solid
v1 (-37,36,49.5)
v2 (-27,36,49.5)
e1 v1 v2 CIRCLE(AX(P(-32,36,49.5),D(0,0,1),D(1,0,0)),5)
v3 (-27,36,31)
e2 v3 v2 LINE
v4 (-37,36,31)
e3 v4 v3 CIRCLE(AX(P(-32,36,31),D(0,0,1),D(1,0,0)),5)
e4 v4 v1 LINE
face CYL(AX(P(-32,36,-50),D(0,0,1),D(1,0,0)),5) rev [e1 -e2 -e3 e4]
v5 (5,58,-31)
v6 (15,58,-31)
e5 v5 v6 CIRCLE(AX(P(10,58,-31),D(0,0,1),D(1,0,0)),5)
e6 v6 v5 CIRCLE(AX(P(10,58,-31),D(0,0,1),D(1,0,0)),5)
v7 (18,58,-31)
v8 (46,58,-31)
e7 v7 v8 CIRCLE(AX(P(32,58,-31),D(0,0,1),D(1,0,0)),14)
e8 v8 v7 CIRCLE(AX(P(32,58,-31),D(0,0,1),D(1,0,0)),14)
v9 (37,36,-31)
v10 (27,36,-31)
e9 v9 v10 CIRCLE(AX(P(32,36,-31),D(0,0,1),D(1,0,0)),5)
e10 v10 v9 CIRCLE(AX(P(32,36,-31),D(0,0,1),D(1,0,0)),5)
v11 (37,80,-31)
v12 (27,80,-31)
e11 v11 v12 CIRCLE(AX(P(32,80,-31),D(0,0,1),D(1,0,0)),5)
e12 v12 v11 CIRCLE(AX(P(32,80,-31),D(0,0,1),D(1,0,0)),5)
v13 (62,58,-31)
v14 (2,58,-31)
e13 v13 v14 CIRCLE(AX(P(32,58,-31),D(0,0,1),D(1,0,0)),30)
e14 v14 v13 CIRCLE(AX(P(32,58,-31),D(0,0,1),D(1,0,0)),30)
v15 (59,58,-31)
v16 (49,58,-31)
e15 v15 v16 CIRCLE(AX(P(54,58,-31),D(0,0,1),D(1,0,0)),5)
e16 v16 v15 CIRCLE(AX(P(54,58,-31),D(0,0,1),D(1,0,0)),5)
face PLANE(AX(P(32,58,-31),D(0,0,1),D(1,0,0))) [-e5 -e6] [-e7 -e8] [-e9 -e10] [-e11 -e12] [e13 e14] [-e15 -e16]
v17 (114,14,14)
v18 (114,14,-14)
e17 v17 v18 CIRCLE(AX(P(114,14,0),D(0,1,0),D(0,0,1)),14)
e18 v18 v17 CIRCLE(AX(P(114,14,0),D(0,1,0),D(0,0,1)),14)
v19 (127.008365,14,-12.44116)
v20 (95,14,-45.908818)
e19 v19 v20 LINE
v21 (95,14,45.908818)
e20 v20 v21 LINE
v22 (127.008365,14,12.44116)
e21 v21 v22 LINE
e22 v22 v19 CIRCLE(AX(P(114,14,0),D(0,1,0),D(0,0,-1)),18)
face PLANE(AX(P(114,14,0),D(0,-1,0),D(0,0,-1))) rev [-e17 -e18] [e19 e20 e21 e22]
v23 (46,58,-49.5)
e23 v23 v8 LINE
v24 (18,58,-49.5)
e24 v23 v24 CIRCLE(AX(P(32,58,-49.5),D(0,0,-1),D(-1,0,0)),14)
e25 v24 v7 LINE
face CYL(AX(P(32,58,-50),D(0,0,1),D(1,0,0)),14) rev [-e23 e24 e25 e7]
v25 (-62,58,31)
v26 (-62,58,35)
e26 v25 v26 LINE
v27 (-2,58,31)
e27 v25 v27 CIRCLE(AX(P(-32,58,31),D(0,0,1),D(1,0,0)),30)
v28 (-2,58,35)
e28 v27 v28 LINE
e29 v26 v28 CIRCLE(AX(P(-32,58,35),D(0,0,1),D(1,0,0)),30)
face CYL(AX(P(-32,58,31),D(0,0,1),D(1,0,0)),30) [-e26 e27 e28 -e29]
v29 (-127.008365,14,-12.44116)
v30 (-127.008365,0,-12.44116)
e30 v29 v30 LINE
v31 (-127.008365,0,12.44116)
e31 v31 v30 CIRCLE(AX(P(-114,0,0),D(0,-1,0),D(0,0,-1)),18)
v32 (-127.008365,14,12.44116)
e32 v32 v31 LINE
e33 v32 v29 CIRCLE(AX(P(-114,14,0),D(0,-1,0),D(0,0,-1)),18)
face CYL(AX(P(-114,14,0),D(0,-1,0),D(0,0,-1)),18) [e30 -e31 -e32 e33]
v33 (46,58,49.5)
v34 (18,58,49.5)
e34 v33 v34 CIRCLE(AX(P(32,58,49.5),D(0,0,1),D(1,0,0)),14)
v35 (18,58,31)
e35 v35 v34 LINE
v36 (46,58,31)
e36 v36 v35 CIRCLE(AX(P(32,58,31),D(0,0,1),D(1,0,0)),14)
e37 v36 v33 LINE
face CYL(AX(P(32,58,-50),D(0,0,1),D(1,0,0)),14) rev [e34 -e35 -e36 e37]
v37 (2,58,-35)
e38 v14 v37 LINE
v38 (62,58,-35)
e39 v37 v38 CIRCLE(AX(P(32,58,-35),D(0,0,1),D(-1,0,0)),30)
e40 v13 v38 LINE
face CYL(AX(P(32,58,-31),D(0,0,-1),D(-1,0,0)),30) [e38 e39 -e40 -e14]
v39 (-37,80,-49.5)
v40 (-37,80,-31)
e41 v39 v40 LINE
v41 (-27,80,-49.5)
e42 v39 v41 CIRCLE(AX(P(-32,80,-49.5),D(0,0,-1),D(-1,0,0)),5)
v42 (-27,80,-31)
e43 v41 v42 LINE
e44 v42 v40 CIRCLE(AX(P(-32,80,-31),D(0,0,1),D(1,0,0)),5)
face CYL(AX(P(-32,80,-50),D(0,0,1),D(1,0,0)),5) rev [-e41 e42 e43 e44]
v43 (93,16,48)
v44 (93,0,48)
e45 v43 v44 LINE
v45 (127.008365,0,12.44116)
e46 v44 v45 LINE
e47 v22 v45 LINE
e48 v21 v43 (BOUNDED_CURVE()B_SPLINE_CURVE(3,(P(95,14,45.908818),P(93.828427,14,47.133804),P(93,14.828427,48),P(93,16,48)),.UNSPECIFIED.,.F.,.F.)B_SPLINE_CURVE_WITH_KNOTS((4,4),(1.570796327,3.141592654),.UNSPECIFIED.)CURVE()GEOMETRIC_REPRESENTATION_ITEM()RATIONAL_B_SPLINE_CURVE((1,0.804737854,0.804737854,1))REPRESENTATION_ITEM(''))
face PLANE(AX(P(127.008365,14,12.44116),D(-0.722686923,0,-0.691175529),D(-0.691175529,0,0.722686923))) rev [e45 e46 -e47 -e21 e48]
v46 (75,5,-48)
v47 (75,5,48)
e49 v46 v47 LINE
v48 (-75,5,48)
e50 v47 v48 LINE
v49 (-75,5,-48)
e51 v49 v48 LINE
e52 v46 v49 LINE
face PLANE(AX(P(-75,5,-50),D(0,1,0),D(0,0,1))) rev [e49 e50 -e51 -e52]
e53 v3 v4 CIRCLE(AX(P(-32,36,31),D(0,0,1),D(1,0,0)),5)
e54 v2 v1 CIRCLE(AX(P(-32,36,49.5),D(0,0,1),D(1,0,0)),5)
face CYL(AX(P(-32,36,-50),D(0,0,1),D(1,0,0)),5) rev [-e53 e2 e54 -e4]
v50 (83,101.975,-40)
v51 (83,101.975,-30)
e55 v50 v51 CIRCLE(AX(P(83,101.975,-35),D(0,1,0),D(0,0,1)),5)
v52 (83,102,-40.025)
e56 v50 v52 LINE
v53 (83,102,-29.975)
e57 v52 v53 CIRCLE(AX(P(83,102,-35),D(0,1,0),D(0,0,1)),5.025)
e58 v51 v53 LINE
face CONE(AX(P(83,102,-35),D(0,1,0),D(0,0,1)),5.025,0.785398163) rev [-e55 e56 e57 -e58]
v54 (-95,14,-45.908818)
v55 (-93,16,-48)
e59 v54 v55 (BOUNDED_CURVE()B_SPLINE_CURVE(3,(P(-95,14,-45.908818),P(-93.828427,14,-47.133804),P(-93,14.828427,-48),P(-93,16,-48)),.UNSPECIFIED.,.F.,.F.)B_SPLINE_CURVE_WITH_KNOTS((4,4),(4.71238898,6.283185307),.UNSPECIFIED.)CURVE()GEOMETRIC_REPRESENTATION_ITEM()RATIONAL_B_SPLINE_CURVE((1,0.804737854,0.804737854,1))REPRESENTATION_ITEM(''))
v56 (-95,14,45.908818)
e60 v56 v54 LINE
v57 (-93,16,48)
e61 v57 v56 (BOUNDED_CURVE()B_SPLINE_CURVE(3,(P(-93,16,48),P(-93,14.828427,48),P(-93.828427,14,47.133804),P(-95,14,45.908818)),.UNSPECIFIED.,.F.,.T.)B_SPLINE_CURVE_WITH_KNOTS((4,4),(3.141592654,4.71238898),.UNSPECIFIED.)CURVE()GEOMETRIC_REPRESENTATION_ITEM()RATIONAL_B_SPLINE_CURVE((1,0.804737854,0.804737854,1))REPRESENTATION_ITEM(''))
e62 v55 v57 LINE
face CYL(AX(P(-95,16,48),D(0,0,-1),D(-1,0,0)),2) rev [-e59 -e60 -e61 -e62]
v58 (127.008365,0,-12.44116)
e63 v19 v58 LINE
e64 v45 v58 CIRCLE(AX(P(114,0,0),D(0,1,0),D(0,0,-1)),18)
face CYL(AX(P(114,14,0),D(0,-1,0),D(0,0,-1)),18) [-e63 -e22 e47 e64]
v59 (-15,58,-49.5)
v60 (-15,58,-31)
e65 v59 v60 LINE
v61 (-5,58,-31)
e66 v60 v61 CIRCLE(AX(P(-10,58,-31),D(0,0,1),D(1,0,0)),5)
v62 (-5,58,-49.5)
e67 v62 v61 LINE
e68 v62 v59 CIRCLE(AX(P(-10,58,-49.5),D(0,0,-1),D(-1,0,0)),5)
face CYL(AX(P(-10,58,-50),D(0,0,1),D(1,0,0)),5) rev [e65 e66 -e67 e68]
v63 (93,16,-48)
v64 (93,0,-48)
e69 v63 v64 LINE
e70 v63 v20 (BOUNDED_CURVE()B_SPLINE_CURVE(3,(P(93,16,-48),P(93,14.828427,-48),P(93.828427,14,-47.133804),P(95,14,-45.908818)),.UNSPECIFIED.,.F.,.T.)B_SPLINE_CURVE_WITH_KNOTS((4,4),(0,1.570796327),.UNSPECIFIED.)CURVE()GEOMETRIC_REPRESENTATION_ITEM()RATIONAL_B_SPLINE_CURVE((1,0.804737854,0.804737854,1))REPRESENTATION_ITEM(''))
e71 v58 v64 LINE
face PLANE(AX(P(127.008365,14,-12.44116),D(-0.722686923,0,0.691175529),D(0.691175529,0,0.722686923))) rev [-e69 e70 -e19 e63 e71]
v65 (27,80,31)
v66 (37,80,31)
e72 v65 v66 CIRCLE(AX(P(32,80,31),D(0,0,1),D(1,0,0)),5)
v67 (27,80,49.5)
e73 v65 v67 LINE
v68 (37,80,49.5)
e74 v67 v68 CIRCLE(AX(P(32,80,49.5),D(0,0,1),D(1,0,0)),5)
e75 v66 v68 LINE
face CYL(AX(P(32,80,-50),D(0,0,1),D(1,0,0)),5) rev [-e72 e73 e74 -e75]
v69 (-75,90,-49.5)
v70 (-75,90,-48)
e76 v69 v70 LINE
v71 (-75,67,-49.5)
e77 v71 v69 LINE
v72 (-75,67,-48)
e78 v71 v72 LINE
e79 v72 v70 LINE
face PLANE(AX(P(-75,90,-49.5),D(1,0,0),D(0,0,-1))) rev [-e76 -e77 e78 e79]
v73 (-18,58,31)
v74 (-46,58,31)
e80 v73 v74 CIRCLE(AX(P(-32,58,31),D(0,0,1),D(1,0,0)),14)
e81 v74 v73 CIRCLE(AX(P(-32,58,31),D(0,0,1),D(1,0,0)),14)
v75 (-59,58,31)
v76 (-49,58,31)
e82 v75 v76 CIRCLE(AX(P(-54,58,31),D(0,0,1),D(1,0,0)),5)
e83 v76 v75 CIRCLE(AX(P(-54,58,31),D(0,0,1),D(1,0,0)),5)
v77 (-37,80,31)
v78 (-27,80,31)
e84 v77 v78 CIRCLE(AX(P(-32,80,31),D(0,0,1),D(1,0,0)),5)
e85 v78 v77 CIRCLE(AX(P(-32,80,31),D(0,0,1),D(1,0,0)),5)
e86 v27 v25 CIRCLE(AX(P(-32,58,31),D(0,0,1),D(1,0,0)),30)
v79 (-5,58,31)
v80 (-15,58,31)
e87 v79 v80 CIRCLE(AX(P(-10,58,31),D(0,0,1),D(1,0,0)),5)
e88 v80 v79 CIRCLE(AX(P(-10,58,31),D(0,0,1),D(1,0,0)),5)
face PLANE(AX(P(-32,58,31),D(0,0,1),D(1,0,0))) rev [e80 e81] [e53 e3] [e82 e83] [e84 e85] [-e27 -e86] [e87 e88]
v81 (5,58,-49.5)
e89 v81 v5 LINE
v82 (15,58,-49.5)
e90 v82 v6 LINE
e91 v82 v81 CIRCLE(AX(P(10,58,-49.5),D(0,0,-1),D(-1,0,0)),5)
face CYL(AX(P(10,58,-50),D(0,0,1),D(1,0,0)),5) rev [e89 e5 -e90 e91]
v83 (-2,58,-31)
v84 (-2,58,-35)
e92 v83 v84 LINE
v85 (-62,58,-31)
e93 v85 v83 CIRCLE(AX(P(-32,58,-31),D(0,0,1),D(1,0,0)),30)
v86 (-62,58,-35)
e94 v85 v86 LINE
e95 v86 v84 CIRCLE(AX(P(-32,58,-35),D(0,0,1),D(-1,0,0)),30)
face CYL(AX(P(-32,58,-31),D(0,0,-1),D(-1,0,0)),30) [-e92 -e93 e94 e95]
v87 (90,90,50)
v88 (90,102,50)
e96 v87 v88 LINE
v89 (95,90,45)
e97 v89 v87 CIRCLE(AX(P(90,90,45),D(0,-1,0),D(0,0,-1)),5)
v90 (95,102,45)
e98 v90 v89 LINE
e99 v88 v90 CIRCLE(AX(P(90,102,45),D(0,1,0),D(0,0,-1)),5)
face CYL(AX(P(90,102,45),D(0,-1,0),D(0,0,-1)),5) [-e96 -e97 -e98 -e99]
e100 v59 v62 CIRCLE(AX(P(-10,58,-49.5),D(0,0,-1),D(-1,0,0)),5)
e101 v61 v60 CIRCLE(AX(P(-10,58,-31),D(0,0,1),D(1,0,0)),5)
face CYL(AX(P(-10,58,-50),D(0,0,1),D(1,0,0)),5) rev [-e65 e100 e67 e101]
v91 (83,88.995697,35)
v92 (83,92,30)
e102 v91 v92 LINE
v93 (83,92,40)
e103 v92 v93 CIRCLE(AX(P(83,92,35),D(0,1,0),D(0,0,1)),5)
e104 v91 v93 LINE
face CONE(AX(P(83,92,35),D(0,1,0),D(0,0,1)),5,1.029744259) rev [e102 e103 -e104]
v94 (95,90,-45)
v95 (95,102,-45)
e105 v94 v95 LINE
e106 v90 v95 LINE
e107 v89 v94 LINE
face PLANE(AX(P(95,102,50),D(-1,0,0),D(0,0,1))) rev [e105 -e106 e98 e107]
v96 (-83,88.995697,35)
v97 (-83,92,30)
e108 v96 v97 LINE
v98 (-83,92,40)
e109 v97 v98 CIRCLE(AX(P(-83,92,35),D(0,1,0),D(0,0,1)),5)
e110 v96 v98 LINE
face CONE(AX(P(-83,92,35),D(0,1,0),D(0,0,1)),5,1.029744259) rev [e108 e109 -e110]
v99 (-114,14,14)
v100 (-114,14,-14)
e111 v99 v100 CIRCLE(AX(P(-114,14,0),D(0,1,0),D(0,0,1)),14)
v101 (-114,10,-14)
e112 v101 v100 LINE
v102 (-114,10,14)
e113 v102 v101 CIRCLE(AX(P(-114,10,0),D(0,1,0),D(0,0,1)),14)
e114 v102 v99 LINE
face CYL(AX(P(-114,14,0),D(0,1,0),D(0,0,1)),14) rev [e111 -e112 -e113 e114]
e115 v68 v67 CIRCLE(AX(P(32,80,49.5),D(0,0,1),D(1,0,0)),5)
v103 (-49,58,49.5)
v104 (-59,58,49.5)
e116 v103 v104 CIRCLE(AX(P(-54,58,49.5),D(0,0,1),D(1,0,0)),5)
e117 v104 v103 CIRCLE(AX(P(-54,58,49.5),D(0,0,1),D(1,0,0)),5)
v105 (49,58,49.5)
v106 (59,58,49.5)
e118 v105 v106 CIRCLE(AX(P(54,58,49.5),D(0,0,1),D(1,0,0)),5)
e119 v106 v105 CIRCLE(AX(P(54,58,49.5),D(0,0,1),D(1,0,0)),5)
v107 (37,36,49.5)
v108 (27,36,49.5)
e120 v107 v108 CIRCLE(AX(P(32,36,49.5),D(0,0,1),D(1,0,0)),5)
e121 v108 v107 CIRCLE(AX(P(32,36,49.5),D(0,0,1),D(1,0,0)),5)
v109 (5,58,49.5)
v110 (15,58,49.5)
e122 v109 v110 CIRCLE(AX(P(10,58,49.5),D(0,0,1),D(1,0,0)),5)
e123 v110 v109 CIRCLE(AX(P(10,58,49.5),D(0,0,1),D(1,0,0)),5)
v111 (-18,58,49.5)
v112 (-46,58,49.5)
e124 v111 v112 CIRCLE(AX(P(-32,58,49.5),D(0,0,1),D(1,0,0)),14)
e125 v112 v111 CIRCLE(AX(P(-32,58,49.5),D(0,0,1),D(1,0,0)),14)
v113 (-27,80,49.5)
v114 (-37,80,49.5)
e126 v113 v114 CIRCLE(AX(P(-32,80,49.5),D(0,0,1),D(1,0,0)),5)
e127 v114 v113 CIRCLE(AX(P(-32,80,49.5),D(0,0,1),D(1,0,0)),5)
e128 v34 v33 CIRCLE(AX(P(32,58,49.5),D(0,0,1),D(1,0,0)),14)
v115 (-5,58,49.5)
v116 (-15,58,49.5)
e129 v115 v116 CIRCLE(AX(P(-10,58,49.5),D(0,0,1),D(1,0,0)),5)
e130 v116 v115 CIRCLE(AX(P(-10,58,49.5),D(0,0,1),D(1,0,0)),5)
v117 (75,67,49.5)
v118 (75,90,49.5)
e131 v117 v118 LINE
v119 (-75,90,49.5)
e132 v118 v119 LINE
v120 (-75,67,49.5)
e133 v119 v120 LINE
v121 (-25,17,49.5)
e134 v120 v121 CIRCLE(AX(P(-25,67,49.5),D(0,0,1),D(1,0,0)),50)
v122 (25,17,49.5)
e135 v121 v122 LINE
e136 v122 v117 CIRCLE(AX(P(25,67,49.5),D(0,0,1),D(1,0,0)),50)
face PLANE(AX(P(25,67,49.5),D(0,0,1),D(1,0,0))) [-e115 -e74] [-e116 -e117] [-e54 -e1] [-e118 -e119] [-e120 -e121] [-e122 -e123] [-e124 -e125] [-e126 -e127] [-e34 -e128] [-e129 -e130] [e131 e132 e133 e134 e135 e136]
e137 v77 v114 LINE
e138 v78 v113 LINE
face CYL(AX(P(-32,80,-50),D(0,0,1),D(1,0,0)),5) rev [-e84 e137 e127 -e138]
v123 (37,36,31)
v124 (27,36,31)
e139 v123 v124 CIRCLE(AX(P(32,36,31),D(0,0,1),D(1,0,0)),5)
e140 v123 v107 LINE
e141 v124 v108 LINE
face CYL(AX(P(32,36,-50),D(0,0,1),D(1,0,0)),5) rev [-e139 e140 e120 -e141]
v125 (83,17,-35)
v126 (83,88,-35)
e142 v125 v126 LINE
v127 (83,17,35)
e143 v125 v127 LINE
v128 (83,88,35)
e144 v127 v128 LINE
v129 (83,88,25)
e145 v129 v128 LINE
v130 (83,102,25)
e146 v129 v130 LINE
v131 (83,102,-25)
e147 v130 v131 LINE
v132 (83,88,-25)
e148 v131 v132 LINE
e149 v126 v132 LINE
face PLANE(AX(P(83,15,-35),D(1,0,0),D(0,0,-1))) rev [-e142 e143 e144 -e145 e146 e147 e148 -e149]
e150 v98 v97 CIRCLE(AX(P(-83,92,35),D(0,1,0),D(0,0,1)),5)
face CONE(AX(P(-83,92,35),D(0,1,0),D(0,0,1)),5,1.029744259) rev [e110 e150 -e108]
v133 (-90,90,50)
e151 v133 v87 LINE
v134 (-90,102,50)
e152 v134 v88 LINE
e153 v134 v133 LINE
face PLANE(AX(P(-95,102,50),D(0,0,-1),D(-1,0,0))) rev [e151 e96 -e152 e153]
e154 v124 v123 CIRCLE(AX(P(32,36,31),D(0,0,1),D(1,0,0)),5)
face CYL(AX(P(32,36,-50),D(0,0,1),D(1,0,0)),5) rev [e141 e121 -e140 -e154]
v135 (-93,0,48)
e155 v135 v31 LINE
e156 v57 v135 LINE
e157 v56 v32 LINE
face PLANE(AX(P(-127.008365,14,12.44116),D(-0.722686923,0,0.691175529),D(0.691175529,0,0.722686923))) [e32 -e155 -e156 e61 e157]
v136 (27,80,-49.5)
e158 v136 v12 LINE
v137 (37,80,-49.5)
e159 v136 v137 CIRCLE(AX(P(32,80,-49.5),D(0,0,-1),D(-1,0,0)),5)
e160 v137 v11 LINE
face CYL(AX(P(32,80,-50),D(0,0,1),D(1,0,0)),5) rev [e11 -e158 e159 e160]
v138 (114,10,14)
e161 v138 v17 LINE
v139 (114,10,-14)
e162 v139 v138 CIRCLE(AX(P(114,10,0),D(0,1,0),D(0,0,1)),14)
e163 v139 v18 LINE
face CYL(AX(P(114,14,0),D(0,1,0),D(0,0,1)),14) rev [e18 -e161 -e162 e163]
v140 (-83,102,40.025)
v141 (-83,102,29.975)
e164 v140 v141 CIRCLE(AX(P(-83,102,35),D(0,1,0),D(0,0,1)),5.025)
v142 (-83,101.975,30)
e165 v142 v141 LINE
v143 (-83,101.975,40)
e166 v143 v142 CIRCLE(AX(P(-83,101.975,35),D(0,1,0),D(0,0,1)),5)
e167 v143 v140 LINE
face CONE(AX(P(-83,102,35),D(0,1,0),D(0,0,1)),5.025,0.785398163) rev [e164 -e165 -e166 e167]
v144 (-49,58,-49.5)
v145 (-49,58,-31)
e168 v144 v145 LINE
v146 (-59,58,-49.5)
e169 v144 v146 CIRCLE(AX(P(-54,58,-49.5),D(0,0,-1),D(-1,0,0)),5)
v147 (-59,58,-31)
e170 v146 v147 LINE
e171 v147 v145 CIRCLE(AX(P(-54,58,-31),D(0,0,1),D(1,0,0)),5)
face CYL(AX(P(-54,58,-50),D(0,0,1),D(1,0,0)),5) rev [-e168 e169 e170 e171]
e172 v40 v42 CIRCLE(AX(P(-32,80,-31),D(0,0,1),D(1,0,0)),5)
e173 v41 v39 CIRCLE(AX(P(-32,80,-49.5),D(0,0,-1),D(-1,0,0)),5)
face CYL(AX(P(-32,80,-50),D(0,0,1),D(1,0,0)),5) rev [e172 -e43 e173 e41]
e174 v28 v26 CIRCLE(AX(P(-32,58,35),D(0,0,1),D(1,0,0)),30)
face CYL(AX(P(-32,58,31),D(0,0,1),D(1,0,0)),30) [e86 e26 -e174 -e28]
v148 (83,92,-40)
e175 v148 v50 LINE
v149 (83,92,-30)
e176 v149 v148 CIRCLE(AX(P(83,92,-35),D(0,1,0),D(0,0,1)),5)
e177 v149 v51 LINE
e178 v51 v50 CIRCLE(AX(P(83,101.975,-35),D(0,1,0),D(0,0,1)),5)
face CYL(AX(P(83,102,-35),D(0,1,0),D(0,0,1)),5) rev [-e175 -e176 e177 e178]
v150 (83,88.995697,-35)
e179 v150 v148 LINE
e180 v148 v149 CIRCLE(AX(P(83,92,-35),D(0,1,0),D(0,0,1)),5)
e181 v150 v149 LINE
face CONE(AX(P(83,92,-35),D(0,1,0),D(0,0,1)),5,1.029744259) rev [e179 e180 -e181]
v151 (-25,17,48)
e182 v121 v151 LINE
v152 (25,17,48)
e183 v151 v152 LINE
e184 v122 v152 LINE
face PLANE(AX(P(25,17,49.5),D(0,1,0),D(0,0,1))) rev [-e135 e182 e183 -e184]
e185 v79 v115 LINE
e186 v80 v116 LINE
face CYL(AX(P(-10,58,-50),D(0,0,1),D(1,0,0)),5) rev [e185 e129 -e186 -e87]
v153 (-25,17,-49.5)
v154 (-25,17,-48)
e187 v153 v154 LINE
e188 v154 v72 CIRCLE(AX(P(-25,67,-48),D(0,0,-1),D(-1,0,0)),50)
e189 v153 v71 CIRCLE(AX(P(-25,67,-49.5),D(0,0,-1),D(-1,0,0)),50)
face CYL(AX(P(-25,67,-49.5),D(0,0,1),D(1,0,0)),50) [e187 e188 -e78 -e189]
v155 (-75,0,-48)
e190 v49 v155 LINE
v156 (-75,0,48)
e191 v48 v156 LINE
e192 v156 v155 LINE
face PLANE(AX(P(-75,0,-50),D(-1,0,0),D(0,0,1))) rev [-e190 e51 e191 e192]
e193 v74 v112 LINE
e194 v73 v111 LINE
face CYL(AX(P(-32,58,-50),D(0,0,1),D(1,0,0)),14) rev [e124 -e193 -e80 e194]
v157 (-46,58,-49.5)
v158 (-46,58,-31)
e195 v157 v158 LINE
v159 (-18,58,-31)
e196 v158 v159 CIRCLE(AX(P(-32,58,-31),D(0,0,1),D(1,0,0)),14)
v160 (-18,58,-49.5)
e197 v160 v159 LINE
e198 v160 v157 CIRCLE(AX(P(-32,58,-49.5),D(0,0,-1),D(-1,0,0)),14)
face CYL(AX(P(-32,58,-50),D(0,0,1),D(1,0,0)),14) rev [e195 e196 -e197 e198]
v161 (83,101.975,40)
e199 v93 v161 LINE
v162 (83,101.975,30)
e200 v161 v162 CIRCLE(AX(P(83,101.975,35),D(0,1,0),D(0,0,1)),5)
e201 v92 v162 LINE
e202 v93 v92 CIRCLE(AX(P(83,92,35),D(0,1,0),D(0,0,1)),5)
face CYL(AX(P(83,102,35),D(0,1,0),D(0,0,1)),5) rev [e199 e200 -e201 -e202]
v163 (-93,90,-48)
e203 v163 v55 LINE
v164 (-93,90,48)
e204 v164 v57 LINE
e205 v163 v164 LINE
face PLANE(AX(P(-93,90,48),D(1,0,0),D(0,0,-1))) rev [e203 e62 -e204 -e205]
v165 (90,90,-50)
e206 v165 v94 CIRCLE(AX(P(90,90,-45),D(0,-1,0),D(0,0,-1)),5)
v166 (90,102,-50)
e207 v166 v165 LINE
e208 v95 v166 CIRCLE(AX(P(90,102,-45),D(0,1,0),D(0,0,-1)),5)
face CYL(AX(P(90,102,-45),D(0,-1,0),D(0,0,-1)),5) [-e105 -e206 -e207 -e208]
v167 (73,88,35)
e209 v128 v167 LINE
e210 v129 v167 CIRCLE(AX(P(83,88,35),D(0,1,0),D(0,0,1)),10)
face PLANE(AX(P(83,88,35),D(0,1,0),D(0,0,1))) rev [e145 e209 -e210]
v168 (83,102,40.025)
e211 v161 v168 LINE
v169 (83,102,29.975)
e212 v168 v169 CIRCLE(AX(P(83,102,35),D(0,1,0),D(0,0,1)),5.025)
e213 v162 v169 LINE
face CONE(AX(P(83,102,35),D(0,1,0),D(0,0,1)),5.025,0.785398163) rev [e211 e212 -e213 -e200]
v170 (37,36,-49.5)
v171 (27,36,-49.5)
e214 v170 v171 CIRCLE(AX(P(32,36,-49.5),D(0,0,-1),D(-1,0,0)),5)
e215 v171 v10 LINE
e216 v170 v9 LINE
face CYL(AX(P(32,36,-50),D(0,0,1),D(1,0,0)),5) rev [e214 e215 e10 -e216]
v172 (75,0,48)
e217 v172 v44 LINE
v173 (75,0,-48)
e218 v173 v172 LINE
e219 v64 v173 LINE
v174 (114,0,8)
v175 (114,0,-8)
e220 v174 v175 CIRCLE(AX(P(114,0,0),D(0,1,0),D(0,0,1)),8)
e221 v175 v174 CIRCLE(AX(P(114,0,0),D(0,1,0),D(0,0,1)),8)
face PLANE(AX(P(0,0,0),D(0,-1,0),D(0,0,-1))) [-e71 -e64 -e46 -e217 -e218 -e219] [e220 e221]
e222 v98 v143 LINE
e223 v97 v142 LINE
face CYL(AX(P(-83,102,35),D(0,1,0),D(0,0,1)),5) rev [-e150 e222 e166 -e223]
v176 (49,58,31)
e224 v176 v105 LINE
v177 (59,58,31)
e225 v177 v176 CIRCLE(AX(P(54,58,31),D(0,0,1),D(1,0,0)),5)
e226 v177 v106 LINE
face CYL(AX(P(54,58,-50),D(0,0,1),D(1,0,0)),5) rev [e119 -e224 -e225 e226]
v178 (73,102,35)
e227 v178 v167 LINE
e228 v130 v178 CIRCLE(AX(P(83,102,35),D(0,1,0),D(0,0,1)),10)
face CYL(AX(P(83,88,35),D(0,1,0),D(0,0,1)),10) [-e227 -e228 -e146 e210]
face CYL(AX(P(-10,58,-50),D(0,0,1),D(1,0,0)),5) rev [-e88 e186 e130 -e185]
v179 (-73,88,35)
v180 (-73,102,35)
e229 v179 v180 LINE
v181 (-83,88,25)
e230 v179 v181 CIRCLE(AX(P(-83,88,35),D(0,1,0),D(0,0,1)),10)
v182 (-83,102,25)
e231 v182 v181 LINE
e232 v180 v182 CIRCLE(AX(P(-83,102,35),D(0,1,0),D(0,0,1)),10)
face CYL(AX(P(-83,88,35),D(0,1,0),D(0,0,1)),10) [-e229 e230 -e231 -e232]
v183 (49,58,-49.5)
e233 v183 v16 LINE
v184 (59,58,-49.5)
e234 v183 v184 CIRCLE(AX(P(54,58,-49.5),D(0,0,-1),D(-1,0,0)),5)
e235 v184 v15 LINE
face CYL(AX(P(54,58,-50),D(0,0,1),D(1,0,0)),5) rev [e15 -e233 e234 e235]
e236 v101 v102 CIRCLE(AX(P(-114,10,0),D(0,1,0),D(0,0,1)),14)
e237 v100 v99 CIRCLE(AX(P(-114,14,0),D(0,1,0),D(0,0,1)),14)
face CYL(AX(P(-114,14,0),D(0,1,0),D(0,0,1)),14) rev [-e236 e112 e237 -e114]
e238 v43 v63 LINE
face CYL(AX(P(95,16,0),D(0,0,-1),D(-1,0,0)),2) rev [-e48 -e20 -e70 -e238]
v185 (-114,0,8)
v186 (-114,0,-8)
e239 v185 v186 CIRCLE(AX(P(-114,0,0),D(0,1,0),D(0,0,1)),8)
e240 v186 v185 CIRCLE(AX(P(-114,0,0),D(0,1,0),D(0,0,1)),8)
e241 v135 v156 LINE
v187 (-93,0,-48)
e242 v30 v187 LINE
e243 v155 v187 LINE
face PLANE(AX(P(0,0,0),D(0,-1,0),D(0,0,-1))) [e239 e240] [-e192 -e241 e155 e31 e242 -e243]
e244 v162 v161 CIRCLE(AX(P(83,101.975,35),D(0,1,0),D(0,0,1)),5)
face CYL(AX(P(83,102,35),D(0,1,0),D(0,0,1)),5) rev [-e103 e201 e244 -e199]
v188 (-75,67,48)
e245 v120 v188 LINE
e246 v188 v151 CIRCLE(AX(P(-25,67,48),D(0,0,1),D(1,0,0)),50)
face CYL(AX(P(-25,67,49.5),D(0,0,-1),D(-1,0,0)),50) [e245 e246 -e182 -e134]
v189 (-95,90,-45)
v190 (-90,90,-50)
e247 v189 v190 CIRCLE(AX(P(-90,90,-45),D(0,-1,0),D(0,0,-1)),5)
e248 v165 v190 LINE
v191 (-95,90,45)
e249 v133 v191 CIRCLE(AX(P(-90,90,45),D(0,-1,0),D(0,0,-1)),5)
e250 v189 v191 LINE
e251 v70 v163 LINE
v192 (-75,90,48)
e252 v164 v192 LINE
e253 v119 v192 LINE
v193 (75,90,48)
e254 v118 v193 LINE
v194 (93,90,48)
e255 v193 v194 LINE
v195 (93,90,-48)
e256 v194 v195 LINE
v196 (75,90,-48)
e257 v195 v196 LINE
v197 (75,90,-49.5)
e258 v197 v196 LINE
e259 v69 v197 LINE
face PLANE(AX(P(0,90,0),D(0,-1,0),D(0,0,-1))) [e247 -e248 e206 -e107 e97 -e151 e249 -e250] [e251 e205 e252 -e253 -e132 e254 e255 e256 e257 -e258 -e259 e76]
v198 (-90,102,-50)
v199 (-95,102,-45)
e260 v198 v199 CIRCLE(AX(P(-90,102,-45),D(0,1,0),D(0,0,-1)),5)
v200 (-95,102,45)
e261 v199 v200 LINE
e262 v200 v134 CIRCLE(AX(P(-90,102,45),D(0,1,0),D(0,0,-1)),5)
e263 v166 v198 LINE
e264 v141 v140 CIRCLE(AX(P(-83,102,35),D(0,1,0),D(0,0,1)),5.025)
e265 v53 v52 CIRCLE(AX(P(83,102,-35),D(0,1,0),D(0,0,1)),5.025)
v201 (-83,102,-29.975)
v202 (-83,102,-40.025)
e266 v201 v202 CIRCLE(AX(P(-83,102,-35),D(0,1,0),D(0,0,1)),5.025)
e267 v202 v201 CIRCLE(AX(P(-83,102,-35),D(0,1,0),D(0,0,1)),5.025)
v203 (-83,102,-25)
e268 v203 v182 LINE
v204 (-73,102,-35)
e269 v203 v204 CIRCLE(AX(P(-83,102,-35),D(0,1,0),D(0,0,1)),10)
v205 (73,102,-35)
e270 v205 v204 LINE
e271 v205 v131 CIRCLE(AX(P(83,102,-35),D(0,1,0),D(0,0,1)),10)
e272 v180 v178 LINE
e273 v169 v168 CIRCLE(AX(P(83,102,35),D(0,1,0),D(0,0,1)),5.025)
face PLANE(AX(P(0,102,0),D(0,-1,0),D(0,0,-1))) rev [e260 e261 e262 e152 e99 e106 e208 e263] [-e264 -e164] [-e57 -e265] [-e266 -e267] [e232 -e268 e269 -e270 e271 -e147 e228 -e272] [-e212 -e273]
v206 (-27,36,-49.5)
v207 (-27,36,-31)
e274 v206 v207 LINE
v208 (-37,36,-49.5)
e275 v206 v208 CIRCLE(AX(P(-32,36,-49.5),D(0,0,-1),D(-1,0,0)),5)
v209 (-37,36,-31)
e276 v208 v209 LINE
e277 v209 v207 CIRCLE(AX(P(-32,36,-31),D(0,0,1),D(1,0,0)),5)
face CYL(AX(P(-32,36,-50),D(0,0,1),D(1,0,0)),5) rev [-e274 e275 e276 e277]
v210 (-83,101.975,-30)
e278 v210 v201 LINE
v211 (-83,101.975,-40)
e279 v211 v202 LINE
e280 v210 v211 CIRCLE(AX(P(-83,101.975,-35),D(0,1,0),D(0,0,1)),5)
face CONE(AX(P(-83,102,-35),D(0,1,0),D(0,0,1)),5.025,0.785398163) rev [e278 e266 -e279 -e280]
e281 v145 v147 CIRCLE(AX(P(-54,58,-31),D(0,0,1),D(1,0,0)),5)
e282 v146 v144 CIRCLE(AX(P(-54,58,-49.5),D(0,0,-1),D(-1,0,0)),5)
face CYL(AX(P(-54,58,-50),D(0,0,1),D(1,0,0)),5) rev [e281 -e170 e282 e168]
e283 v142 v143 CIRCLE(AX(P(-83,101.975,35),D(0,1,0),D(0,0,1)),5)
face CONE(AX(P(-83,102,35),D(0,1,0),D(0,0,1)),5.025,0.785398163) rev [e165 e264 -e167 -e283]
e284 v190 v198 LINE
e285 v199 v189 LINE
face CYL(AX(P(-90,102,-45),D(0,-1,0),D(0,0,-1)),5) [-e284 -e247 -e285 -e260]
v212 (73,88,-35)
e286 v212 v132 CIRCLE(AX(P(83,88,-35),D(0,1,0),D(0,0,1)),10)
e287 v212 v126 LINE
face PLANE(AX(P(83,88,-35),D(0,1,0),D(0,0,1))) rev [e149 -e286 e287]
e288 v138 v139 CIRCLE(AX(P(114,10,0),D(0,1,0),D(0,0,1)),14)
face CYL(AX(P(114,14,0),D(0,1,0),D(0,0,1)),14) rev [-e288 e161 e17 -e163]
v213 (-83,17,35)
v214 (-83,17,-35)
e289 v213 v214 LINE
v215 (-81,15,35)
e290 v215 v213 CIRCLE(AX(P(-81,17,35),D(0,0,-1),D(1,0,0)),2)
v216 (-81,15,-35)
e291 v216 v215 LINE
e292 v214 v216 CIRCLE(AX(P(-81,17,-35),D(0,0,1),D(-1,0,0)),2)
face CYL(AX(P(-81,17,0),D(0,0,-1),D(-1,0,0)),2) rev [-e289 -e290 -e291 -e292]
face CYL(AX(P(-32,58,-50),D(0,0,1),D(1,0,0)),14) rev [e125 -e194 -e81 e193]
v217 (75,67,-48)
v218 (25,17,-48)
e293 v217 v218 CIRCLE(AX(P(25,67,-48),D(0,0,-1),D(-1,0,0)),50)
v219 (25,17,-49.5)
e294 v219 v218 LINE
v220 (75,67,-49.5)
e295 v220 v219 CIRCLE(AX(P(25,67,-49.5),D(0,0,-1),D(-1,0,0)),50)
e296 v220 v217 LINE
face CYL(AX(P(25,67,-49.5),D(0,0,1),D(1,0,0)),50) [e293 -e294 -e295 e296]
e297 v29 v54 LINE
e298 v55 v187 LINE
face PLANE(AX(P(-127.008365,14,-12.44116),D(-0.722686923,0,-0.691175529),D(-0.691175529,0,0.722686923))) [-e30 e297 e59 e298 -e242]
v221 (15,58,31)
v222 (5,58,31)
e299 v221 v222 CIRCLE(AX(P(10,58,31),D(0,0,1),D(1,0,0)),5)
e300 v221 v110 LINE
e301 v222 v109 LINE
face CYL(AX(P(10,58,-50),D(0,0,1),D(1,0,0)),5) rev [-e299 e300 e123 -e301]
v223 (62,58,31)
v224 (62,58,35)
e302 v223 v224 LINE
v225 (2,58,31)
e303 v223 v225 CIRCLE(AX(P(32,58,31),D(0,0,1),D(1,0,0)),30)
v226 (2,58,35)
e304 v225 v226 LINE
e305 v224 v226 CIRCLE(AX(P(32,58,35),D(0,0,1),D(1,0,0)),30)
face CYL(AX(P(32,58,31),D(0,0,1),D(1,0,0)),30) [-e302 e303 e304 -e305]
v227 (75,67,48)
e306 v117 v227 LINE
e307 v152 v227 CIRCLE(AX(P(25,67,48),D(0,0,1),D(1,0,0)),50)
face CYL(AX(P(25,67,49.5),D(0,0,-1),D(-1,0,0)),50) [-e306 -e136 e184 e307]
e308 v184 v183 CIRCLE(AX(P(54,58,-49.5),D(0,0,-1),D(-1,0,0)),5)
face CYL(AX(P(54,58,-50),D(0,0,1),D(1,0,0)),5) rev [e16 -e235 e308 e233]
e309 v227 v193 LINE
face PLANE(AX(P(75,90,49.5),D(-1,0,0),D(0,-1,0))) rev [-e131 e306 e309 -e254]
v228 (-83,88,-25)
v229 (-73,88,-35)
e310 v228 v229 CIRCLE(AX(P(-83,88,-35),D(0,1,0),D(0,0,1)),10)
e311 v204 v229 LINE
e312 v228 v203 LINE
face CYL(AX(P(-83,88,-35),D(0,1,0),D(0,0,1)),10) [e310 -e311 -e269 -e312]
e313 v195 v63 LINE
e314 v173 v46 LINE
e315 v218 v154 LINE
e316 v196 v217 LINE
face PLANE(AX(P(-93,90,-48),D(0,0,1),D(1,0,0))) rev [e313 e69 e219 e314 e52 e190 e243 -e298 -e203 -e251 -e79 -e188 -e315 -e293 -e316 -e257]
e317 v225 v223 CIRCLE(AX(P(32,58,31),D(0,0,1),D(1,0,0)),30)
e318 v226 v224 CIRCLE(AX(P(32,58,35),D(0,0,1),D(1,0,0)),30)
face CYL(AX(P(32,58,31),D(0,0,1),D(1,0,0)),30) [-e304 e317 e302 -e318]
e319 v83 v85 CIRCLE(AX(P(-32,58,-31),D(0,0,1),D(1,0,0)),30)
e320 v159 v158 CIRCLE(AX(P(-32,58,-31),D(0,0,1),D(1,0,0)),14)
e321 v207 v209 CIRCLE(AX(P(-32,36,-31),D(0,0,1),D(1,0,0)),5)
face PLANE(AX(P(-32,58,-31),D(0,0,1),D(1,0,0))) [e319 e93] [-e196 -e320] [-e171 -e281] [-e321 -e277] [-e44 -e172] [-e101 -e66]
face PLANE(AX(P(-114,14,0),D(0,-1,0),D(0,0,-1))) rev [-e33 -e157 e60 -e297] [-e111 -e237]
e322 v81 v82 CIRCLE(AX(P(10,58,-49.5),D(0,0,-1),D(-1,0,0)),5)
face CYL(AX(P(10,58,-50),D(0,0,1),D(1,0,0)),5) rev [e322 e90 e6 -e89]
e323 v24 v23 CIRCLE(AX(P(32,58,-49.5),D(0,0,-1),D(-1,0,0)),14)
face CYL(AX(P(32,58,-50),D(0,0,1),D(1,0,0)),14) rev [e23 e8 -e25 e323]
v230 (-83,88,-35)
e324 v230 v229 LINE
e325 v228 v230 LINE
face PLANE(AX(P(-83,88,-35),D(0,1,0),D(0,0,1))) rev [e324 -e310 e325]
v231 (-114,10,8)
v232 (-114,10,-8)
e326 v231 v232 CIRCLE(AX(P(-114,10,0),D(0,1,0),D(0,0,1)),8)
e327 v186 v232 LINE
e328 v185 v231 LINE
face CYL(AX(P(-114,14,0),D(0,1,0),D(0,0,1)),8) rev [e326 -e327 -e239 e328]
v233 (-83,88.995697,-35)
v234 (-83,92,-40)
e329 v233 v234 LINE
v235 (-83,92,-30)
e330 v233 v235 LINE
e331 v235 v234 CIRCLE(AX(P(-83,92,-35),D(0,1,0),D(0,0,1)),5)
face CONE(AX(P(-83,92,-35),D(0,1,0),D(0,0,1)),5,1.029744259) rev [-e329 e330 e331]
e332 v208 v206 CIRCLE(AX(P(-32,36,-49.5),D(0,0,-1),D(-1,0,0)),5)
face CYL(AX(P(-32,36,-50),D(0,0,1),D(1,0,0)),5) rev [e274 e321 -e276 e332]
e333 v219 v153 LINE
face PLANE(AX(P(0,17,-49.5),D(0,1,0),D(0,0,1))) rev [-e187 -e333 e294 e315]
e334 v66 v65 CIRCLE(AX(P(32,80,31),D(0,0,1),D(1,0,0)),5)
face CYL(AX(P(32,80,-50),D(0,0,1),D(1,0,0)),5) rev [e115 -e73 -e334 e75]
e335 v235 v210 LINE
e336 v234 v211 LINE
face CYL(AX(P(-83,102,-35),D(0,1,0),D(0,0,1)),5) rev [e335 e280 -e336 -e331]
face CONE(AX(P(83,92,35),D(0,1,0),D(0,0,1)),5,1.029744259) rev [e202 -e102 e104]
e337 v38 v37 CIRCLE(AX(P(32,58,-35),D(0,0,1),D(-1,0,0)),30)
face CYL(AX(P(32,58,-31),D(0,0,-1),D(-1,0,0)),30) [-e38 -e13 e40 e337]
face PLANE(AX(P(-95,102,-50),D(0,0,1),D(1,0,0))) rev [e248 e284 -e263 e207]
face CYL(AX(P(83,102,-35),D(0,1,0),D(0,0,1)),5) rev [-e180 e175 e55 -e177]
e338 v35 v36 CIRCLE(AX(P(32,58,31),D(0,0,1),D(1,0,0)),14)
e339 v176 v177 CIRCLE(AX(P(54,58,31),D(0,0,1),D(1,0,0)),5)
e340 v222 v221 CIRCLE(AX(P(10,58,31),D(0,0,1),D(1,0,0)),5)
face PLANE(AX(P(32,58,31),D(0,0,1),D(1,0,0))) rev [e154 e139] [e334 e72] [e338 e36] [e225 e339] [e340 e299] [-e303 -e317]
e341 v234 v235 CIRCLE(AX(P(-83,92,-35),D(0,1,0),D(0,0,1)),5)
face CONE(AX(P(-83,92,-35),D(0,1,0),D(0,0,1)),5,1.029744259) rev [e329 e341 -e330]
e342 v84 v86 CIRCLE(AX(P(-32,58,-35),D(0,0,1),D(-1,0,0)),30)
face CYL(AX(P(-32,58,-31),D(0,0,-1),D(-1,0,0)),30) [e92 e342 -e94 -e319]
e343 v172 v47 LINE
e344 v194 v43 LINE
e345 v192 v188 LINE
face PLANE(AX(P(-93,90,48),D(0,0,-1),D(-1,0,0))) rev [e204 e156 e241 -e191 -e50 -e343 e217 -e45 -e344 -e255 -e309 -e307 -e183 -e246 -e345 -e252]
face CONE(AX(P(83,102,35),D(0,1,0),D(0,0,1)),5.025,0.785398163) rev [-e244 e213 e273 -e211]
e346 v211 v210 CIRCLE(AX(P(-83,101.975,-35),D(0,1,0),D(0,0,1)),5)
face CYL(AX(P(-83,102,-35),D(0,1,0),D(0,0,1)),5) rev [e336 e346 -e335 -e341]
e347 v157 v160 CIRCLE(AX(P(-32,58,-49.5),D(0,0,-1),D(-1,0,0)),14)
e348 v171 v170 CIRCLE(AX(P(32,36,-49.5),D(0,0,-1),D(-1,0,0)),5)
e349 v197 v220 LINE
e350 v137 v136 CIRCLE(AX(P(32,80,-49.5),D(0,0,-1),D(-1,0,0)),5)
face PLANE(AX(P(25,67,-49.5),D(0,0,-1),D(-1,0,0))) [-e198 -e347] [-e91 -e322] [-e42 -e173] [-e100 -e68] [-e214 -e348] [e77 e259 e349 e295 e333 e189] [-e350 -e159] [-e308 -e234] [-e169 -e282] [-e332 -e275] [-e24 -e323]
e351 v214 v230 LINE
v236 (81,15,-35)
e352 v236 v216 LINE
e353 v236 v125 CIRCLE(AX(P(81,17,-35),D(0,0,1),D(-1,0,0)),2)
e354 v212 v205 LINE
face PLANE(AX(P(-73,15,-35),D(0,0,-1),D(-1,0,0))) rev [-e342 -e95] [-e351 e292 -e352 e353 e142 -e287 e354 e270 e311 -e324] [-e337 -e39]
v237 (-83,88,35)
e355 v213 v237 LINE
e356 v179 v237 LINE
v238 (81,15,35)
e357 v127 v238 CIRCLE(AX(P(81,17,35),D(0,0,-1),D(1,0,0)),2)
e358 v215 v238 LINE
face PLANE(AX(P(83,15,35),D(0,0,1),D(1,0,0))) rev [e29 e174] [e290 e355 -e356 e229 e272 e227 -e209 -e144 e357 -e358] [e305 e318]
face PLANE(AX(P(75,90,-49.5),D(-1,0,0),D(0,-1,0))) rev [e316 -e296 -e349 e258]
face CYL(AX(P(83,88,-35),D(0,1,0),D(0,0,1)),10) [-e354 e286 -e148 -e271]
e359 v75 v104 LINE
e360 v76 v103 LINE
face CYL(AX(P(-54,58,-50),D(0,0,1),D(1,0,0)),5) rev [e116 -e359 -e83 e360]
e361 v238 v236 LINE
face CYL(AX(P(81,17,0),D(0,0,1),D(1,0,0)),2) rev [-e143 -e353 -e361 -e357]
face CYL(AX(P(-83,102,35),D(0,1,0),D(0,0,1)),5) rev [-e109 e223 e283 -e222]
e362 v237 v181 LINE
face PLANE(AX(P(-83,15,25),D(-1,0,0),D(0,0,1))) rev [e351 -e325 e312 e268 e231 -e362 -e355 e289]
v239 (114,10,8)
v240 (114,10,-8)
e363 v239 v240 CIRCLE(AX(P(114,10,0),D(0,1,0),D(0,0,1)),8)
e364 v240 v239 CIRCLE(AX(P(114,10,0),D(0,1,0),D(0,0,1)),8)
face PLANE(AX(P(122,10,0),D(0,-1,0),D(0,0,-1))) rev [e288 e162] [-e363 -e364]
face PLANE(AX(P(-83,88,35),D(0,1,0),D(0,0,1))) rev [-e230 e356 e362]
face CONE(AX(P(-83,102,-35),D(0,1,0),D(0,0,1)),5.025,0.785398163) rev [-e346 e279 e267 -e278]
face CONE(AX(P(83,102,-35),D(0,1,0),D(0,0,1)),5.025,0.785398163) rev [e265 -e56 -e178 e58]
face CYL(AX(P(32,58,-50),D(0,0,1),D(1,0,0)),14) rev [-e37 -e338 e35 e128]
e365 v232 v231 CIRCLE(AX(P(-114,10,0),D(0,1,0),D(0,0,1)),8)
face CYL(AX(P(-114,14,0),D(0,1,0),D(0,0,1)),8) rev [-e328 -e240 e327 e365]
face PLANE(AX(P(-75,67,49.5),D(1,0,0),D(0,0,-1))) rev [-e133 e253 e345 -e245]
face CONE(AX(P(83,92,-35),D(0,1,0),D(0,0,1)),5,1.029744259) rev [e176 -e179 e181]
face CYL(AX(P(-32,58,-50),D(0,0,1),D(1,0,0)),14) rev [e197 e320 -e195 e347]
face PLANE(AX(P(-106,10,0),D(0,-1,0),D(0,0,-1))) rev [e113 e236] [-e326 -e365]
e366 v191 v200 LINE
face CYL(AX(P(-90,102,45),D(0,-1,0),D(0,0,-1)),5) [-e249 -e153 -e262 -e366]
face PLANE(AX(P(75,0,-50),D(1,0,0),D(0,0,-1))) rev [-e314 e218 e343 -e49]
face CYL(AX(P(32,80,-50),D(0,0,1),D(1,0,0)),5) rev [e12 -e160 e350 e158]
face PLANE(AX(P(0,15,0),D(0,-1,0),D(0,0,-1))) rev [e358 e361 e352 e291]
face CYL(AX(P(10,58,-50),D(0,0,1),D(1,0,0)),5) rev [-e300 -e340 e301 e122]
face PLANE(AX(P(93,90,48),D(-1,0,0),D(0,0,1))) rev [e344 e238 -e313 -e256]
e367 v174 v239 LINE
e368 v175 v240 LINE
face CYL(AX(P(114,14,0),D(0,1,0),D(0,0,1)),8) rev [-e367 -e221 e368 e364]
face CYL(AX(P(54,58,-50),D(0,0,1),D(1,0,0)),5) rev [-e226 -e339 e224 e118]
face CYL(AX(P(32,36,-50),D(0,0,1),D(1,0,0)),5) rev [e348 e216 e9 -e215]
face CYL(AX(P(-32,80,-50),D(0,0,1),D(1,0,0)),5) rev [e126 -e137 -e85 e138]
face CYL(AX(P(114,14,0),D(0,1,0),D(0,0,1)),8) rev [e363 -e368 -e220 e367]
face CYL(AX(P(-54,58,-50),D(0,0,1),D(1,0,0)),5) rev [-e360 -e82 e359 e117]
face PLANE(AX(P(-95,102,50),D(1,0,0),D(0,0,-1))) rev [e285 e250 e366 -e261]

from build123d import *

# Parameters (mm, degrees)
HOUSING_BODY_SKETCH_W                   = 186
HOUSING_BODY_SKETCH_H                   = 96
HOUSING_BODY_186X96X90_DEPTH            = 90
TOP_FLANGE_SKETCH_W                     = 190
TOP_FLANGE_SKETCH_H                     = 100
TOP_FLANGE_190X100X12_DEPTH             = 12
BASE_RECESS_SKETCH_W                    = 150
BASE_RECESS_SKETCH_H                    = 5
BASE_RECESS_DEPTH                       = 171.390727447
MOUNTING_FEET_DEPTH                     = 14
FOOT_HOLE_CBORE_16_D                    = 16
FOOT_HOLE_CBORE_16_CBORE_D              = 28
FOOT_HOLE_CBORE_16_CBORE_DEPTH          = 4
FLANGE_FILLET_R5_R                      = 5
INNER_CAVITY_DEPTH                      = 87
DOWEL_BOSS_SKETCH_R                     = 10
DOWEL_BOSS_20_DEPTH                     = 14
DOWEL_HOLE_10_D                         = 10
DOWEL_HOLE_10_DEPTH                     = 10
DOWEL_HOLE_10_CSINK_D                   = 10.05
DOWEL_HOLE_10_CSINK_ANGLE               = 90
DOWEL_HOLE_10_TIP                       = 3.004303095
BEARING_BOSSES_SIDE_1_SKETCH_R          = 30
BEARING_BOSSES_SIDE_1_DEPTH             = 15
BEARING_START                           = -15
BEARING_BOSSES_SIDE_2_SKETCH_R          = 30
BEARING_BOSSES_SIDE_2_DEPTH             = 15
SIDE_PAD_1_5MM_DEPTH                    = 1.5
RAISED_START                            = 1.5
RAISED_PAD_1_5MM_DEPTH                  = 1.5
BEARING_BORES_AND_BOLT_HOLES_SKETCH_R   = 5
BEARING_BORES_AND_BOLT_HOLES_SKETCH_R_2 = 14
BEARING_BORES_AND_BOLT_HOLES_DEPTH      = 195.237612218
EDGE_FILLETS_R2_R                       = 2


with BuildPart() as part:
    # Housing Body Sketch → Housing Body 186x96x90 (new body)
    with BuildSketch(Plane(origin=(0, 0, 0), x_dir=(1, 0, 0), z_dir=(0, 1, 0))):
        Rectangle(HOUSING_BODY_SKETCH_W, HOUSING_BODY_SKETCH_H)
    extrude(amount=HOUSING_BODY_186X96X90_DEPTH)

    # Top Flange Sketch → Top Flange 190x100x12 (add)
    with BuildSketch(Plane(origin=(0, 90, 0), x_dir=(1, 0, 0), z_dir=(0, 1, 0))):
        Rectangle(TOP_FLANGE_SKETCH_W, TOP_FLANGE_SKETCH_H)
    extrude(amount=TOP_FLANGE_190X100X12_DEPTH)

    # Base Recess Sketch → Base Recess (cut, through all)
    with BuildSketch(Plane.XY.offset(48)):
        with Locations((0, 2.5)):
            Rectangle(BASE_RECESS_SKETCH_W, BASE_RECESS_SKETCH_H)
    extrude(amount=-BASE_RECESS_DEPTH, mode=Mode.SUBTRACT)

    # Mounting Feet Sketch → Mounting Feet (add)
    with BuildSketch(Plane.XZ):
        with BuildLine():
            Line((-127.008364611, 12.441159517), (-93, 48))
            Line((-93, 48), (-93, -48))
            Line((-93, -48), (-127.008364611, -12.441159517))
            ThreePointArc((-127.008364611, -12.441159517), (-132, 0), (-127.008364611, 12.441159517))
        make_face()
    mounting_feet = extrude(amount=-MOUNTING_FEET_DEPTH)

    # Foot Hole CBore Ø16 (through all)
    with Locations(Plane(origin=(0, 14, 0), x_dir=(1, 0, 0), z_dir=(0, 1, 0))):
        with Locations((-114, 0)):
            foot_hole_cbore_16 = CounterBoreHole(FOOT_HOLE_CBORE_16_D / 2, FOOT_HOLE_CBORE_16_CBORE_D / 2, FOOT_HOLE_CBORE_16_CBORE_DEPTH)

    # Foot Hole Mirror: Mounting Feet, Foot Hole CBore Ø16 across plane
    add(mounting_feet.mirror(Plane(origin=(0, 0, 0), x_dir=(0, 0, 1), z_dir=(1, 0, 0))))
    add(foot_hole_cbore_16.mirror(Plane(origin=(0, 0, 0), x_dir=(0, 0, 1), z_dir=(1, 0, 0))), mode=Mode.SUBTRACT)

    # Flange Fillet R5
    flange_fillet_r5_edges = [part.edges().sort_by_distance(p)[0] for p in [
        (95, 96, 50),
        (95, 96, -50),
        (-95, 96, -50),
        (-95, 96, 50),
    ]]
    fillet(flange_fillet_r5_edges, radius=FLANGE_FILLET_R5_R)

    # Inner Cavity Sketch → Inner Cavity (cut)
    with BuildSketch(Plane(origin=(0, 102, 0), x_dir=(1, 0, 0), z_dir=(0, 1, 0))):
        Polygon((-73, 35), (73, 35), (83, 35), (83, 25), (83, -25), (83, -35), (73, -35), (-73, -35), (-83, -35), (-83, -25), (-83, 25), (-83, 35), align=None)
    extrude(amount=-INNER_CAVITY_DEPTH, mode=Mode.SUBTRACT)

    # Dowel Boss Sketch → Dowel Boss Ø20 (add)
    with BuildSketch(Plane(origin=(0, 102, 0), x_dir=(1, 0, 0), z_dir=(0, 1, 0))):
        with Locations((-83, 35)):
            Circle(DOWEL_BOSS_SKETCH_R)
        with Locations((83, 35)):
            Circle(DOWEL_BOSS_SKETCH_R)
        with Locations((83, -35)):
            Circle(DOWEL_BOSS_SKETCH_R)
        with Locations((-83, -35)):
            Circle(DOWEL_BOSS_SKETCH_R)
    extrude(amount=-DOWEL_BOSS_20_DEPTH)

    # Dowel Hole Ø10
    with Locations(Plane(origin=(0, 102, 0), x_dir=(1, 0, 0), z_dir=(0, 1, 0))):
        with Locations((-83, -35), (-83, 35), (83, 35), (83, -35)):
            CounterSinkHole(DOWEL_HOLE_10_D / 2, DOWEL_HOLE_10_CSINK_D / 2, depth=DOWEL_HOLE_10_DEPTH, counter_sink_angle=DOWEL_HOLE_10_CSINK_ANGLE)
            with Locations((0, 0, -(DOWEL_HOLE_10_DEPTH + DOWEL_HOLE_10_TIP / 2))):  # 118° drill point
                Cone(0, DOWEL_HOLE_10_D / 2, DOWEL_HOLE_10_TIP, mode=Mode.SUBTRACT)

    # Bearing Bosses Side 1 Sketch → Bearing Bosses Side 1 (add)
    with BuildSketch(Plane.XY.offset(-46)):
        with Locations(Location((-32, 58, 0), (0, 0, 180))):
            Circle(BEARING_BOSSES_SIDE_1_SKETCH_R)
        with Locations(Location((32, 58, 0), (0, 0, 180))):
            Circle(BEARING_BOSSES_SIDE_1_SKETCH_R)
    extrude(amount=BEARING_BOSSES_SIDE_1_DEPTH)

    # Bearing Bosses Side 2 Sketch → Bearing Bosses Side 2 (add)
    with BuildSketch(Plane.XY.offset(46).offset(BEARING_START)):
        with Locations(Location((32, 58, 0), (0, 0, 180))):
            Circle(BEARING_BOSSES_SIDE_2_SKETCH_R)
        with Locations(Location((-32, 58, 0), (0, 0, 180))):
            Circle(BEARING_BOSSES_SIDE_2_SKETCH_R)
    extrude(amount=BEARING_BOSSES_SIDE_2_DEPTH)

    # Side Pad Sketch → Side Pad 1.5mm (add)
    with BuildSketch(Plane(origin=(0, 0, -48), x_dir=(-1, 0, 0), z_dir=(0, 0, -1))):
        with BuildLine():
            Line((-25, 17), (0, 17))
            Line((0, 17), (25, 17))
            ThreePointArc((25, 17), (60.355339059, 31.644660941), (75, 67))
            Line((75, 67), (75, 90))
            Line((75, 90), (-75, 90))
            Line((-75, 90), (-75, 67))
            ThreePointArc((-75, 67), (-60.355339059, 31.644660941), (-25, 17))
        make_face()
    extrude(amount=SIDE_PAD_1_5MM_DEPTH)

    # Raised Pad Sketch → Raised Pad 1.5mm (add)
    with BuildSketch(Plane.XY.offset(48).offset(RAISED_START)):
        with BuildLine():
            Line((75, 90), (75, 67))
            ThreePointArc((75, 67), (60.355339059, 31.644660941), (25, 17))
            Line((25, 17), (-25, 17))
            ThreePointArc((-25, 17), (-60.355339059, 31.644660941), (-75, 67))
            Line((-75, 67), (-75, 90))
            Line((-75, 90), (75, 90))
        make_face()
    extrude(amount=-RAISED_PAD_1_5MM_DEPTH)

    # Bearing Bores and Bolt Holes Sketch → Bearing Bores and Bolt Holes (cut, through all)
    with BuildSketch(Plane.XY.offset(49.5)):
        with Locations((-32, 80)):
            Circle(BEARING_BORES_AND_BOLT_HOLES_SKETCH_R)
        with Locations((32, 80)):
            Circle(BEARING_BORES_AND_BOLT_HOLES_SKETCH_R)
        with Locations((-32, 58)):
            Circle(BEARING_BORES_AND_BOLT_HOLES_SKETCH_R_2)
        with Locations((32, 58)):
            Circle(BEARING_BORES_AND_BOLT_HOLES_SKETCH_R_2)
        with Locations((-10, 58)):
            Circle(BEARING_BORES_AND_BOLT_HOLES_SKETCH_R)
        with Locations((-32, 36)):
            Circle(BEARING_BORES_AND_BOLT_HOLES_SKETCH_R)
        with Locations((-54, 58)):
            Circle(BEARING_BORES_AND_BOLT_HOLES_SKETCH_R)
        with Locations((54, 58)):
            Circle(BEARING_BORES_AND_BOLT_HOLES_SKETCH_R)
        with Locations((32, 36)):
            Circle(BEARING_BORES_AND_BOLT_HOLES_SKETCH_R)
        with Locations((10, 58)):
            Circle(BEARING_BORES_AND_BOLT_HOLES_SKETCH_R)
    extrude(amount=-BEARING_BORES_AND_BOLT_HOLES_DEPTH, mode=Mode.SUBTRACT)

    # Edge Fillets R2
    edge_fillets_r2_edges = [part.edges().sort_by_distance(p)[0] for p in [
        (83, 15, 0),
        (-83, 15, 0),
        (-93, 14, 0),
        (93, 14, 0),
    ]]
    fillet(edge_fillets_r2_edges, radius=EDGE_FILLETS_R2_R)


solid = part.part
